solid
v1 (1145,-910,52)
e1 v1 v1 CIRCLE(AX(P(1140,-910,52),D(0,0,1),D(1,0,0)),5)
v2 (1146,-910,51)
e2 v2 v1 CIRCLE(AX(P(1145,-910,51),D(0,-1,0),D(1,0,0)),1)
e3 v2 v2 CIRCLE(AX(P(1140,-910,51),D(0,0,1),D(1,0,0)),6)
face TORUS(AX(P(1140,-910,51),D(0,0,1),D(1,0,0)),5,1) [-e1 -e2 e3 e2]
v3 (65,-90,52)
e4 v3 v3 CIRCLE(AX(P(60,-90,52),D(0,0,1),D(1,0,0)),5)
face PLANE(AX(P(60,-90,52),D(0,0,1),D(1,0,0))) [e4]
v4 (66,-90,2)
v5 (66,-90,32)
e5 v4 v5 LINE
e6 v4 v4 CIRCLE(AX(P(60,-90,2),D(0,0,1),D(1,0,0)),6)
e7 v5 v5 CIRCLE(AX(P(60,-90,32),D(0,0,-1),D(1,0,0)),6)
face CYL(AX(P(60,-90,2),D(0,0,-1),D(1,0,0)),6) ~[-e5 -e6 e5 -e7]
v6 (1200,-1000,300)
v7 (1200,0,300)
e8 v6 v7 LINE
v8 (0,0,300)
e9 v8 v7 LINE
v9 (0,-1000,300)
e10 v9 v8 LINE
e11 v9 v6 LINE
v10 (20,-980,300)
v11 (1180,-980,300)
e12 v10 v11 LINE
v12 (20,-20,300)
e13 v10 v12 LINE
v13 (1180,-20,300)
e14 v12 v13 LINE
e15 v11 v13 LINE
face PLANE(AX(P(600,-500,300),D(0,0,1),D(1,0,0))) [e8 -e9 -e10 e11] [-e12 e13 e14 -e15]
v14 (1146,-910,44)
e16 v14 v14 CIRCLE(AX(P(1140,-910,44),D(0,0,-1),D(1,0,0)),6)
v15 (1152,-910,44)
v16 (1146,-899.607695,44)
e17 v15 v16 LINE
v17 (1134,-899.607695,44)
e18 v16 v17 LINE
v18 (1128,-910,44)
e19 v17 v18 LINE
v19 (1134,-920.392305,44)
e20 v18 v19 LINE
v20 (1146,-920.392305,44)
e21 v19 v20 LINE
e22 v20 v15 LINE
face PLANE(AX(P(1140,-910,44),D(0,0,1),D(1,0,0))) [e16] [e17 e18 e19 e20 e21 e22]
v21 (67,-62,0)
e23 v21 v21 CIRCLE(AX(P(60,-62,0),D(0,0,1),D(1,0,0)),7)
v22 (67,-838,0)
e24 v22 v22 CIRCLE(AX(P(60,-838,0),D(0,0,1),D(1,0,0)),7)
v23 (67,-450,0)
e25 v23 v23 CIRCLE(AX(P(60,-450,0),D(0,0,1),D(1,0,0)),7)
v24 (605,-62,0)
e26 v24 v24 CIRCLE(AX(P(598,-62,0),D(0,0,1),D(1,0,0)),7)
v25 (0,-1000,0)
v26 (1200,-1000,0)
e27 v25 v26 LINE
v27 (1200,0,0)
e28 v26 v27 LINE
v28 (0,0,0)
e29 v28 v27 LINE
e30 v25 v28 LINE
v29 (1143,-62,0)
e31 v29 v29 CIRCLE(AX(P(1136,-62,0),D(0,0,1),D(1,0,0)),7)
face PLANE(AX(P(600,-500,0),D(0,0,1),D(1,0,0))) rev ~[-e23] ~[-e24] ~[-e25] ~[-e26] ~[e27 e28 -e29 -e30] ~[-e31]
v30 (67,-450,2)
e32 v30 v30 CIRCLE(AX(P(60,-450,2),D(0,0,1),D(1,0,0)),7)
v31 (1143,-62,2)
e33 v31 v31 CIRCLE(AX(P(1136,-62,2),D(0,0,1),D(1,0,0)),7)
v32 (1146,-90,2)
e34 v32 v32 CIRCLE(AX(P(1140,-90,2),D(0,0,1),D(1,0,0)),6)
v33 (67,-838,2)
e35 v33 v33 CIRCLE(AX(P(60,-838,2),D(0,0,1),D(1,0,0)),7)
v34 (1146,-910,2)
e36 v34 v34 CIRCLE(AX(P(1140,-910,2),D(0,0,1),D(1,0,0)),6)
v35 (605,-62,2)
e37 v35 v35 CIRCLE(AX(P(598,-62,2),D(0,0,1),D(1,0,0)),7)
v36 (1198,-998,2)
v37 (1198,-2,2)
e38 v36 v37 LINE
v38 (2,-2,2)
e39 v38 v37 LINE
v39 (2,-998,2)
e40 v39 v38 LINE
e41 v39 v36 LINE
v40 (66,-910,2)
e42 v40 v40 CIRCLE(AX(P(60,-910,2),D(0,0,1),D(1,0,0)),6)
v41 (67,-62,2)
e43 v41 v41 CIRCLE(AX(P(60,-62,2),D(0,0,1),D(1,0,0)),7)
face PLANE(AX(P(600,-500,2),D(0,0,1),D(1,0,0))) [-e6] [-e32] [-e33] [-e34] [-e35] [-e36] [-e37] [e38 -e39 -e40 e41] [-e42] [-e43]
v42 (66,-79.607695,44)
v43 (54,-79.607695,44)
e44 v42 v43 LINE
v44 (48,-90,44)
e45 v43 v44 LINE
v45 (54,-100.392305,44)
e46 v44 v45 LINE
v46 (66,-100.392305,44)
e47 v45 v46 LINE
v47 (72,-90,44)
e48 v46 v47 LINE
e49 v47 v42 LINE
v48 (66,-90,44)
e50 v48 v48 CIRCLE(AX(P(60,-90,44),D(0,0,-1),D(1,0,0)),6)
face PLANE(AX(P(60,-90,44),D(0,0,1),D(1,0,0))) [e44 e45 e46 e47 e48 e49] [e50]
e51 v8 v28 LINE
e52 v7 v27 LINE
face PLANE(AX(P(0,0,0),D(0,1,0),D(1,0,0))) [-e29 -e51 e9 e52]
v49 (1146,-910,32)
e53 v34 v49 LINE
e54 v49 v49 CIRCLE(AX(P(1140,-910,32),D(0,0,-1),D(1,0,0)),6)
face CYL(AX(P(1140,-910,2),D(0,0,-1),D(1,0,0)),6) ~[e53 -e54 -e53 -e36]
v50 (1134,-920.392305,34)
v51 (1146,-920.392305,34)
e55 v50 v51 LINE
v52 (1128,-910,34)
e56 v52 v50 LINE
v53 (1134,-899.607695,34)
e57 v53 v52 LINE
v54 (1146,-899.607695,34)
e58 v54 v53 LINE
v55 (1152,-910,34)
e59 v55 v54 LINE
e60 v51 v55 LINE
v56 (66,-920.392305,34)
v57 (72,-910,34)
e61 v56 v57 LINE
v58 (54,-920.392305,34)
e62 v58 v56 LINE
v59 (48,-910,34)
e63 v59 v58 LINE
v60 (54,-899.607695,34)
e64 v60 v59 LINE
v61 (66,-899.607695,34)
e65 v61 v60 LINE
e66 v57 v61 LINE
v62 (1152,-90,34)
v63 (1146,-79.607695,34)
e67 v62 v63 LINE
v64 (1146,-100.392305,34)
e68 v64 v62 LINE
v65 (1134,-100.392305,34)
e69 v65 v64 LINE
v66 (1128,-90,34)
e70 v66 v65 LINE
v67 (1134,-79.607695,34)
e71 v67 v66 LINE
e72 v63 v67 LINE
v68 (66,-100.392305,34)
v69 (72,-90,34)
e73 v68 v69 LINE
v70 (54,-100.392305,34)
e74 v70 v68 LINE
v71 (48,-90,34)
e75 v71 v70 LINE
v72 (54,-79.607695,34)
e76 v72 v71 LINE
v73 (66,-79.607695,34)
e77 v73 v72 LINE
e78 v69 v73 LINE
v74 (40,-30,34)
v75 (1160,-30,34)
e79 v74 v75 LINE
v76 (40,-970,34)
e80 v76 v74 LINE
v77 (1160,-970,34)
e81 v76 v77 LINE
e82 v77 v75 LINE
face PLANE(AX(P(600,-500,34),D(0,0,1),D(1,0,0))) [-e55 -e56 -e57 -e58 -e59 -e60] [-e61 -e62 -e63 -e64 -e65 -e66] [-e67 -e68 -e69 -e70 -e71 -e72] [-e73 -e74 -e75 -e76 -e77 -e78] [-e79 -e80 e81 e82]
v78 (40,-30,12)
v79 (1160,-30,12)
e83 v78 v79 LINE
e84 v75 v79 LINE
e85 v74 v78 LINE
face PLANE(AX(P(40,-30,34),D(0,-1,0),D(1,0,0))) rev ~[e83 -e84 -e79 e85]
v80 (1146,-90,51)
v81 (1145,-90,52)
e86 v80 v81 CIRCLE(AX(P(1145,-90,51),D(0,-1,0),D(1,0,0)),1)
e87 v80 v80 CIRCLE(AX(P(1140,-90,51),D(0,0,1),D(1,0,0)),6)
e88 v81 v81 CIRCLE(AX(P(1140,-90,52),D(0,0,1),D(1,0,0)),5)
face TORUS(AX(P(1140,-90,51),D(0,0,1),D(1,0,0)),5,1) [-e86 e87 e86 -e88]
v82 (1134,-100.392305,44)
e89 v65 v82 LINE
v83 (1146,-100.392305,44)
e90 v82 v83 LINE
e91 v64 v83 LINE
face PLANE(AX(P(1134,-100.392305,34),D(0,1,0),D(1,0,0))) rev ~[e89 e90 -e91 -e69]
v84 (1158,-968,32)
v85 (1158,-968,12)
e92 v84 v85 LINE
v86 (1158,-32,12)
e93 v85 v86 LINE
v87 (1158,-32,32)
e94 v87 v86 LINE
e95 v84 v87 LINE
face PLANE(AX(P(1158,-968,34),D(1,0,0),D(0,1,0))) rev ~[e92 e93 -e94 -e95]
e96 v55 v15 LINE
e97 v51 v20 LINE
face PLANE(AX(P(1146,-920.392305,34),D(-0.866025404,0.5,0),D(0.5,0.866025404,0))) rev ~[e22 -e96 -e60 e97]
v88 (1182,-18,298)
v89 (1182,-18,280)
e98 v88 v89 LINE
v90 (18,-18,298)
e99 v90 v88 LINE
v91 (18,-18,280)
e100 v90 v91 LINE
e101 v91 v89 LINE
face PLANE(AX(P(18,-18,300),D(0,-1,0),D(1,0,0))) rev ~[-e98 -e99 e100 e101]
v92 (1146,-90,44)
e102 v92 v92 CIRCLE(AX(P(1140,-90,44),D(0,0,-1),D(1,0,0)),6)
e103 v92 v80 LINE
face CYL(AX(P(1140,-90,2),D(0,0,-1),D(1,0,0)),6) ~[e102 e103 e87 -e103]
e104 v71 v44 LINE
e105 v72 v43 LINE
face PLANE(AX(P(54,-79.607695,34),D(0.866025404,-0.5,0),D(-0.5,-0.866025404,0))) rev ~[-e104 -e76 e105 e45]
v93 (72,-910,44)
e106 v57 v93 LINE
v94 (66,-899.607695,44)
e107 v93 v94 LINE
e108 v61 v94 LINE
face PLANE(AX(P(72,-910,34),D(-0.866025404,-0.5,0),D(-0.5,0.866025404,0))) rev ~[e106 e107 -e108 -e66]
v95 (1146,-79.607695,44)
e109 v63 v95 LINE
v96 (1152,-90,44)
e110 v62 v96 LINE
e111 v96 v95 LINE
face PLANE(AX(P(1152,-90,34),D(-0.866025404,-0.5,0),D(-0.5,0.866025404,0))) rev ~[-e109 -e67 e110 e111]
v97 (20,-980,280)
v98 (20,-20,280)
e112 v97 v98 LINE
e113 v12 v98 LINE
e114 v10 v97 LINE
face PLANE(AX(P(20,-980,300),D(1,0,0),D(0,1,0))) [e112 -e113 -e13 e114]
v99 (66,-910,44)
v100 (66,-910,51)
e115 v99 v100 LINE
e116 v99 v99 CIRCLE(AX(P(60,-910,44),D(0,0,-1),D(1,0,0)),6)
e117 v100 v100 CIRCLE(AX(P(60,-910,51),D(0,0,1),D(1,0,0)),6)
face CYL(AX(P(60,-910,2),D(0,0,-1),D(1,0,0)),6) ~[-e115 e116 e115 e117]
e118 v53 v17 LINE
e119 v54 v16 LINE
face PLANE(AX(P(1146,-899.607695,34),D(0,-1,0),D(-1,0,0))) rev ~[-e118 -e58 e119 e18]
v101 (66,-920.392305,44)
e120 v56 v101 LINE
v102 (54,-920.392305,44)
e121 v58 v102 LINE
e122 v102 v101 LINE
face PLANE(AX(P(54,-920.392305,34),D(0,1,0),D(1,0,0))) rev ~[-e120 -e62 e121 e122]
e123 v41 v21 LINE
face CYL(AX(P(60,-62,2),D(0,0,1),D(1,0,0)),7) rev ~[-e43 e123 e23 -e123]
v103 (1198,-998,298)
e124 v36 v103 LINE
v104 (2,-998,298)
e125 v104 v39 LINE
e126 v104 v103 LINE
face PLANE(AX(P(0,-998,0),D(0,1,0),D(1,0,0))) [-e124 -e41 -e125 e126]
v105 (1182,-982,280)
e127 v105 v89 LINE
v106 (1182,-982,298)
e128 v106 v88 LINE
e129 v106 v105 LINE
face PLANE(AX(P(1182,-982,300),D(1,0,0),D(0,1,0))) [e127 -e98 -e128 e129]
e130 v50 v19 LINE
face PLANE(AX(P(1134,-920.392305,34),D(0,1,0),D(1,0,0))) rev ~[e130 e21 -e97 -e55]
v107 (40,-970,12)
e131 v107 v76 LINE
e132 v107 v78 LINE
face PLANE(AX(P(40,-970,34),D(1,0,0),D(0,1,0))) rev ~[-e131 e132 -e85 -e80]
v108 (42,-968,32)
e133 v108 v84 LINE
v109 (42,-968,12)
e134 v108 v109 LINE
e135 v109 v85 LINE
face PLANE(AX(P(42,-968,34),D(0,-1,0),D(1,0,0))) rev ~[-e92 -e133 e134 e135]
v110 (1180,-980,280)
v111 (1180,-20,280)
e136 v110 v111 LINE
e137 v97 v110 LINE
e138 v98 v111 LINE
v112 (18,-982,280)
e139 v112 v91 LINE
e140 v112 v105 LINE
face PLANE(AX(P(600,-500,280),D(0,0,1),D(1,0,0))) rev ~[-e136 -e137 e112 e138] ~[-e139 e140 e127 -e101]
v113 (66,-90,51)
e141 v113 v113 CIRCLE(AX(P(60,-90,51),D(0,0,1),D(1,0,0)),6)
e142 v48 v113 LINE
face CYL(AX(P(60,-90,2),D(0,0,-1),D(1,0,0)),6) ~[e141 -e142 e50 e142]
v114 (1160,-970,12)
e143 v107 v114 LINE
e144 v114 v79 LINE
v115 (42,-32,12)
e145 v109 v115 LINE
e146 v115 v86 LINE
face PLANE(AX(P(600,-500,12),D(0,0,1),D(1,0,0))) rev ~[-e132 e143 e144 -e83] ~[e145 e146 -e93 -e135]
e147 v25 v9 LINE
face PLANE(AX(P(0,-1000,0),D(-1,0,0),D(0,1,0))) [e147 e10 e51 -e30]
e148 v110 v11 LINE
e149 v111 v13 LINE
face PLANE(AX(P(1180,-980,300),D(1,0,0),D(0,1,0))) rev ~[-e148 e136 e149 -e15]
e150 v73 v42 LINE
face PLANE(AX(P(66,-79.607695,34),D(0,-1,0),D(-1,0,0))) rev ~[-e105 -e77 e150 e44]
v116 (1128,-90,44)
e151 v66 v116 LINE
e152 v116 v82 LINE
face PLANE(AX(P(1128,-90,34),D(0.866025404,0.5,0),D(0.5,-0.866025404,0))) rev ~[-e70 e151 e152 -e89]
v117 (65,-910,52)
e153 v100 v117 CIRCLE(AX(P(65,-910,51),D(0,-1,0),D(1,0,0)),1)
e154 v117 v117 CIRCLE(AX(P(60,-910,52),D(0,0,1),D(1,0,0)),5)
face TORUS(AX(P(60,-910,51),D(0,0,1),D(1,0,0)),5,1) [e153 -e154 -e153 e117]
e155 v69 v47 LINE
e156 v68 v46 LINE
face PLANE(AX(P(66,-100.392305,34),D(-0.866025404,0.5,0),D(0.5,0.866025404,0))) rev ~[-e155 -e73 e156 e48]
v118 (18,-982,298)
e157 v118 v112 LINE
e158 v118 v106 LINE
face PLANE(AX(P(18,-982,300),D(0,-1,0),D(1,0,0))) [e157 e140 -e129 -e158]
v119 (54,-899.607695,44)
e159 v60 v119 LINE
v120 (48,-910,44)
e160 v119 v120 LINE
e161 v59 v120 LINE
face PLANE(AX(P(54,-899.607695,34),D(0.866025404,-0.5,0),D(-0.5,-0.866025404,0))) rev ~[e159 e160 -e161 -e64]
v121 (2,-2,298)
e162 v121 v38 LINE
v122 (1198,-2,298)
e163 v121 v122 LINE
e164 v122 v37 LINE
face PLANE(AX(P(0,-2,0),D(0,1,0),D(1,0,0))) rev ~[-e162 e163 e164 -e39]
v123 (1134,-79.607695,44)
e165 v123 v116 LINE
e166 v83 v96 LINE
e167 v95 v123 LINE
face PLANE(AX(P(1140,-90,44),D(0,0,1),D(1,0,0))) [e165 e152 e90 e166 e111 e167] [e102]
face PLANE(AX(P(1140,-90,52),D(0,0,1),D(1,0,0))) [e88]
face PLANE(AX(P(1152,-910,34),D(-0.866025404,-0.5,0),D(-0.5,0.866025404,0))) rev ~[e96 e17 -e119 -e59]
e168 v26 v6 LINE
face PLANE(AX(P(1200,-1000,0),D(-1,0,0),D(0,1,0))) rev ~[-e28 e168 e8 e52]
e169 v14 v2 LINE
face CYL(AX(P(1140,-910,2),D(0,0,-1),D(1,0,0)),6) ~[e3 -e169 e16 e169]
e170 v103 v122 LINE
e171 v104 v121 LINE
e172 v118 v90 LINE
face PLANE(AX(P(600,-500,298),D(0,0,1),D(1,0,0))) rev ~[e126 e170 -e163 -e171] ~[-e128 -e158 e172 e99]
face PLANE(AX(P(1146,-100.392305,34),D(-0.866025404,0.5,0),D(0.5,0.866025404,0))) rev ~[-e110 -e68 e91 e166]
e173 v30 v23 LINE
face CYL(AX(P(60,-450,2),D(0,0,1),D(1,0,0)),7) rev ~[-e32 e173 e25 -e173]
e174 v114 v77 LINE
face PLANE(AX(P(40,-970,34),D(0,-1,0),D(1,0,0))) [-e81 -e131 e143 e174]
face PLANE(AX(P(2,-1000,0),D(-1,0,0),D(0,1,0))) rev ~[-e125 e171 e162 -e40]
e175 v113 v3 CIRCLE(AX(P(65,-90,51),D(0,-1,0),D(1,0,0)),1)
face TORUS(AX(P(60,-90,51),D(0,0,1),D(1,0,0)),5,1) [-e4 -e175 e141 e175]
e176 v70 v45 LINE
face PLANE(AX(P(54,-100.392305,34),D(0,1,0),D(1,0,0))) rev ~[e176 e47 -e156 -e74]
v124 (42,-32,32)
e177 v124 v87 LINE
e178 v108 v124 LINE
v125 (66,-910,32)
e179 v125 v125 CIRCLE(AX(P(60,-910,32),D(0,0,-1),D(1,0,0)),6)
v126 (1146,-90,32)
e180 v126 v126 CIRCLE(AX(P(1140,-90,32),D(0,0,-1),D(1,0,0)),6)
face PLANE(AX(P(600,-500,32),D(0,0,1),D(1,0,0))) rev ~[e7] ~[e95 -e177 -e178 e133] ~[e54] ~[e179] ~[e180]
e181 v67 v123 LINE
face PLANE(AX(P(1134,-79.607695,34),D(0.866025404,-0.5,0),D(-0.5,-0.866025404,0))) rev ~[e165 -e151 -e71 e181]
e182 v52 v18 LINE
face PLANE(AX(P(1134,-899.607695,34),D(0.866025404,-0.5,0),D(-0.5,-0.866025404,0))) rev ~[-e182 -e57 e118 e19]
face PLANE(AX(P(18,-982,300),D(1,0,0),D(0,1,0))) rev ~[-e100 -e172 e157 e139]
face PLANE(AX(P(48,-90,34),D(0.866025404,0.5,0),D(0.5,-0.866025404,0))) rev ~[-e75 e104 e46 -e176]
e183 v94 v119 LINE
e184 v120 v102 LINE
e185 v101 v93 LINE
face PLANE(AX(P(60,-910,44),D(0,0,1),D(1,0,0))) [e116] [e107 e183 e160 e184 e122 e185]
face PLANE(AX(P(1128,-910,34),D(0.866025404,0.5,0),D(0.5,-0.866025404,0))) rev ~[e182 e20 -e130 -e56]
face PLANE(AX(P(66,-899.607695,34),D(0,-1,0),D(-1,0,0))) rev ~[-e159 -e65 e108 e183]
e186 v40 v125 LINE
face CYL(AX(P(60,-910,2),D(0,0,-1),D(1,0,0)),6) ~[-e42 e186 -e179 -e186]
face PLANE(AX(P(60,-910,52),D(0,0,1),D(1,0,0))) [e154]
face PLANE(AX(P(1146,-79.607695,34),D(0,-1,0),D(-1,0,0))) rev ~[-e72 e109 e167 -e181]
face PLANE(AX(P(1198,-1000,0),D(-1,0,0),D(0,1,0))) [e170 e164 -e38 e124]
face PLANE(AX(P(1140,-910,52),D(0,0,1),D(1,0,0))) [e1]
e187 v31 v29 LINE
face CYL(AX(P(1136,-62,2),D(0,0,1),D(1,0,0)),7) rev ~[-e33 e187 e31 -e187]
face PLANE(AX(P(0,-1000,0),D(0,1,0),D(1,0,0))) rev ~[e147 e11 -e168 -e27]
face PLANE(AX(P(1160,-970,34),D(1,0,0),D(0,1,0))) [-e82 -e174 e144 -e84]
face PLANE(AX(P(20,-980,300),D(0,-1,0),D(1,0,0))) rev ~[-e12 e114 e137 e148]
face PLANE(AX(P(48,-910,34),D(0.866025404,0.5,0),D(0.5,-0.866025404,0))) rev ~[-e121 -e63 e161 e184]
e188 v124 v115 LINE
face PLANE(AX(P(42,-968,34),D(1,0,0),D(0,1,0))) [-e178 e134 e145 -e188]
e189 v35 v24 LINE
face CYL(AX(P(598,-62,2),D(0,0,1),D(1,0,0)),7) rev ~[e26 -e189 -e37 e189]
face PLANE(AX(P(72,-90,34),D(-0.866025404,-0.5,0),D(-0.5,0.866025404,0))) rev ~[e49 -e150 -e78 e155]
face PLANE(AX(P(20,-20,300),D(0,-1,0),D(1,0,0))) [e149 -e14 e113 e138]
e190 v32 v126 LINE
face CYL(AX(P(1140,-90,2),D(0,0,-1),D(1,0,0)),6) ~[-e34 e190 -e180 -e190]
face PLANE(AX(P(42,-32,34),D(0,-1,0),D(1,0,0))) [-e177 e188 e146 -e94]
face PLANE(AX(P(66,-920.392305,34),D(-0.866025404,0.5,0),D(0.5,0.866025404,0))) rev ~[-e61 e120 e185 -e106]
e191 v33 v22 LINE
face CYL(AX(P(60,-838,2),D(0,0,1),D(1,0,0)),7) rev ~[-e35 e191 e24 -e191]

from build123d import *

# Parameters (mm, degrees)
SKETCH_1_W                     = 1200
SKETCH_1_H                     = 1000
EXTRUDE_1_DEPTH                = 300
SHELL_1_T                      = -2
SKETCH_2_R                     = 7
CUT_EXTRUDE_1_DEPTH            = 1591.221368238
PATTERN_LINEAR_1_COUNT         = 3
PATTERN_LINEAR_1_PITCH         = 388
PATTERN_LINEAR_2_COUNT         = 3
PATTERN_LINEAR_2_PITCH         = 538
SKETCH_3_W                     = 1200
SKETCH_3_H                     = 1000
SKETCH_3_W_2                   = 1160
SKETCH_3_H_2                   = 960
EXTRUDE_2_DEPTH                = 2
SKETCH_4_W                     = 1164
SKETCH_4_H                     = 964
SKETCH_4_W_2                   = 1160
SKETCH_4_H_2                   = 960
EXTRUDE_3_DEPTH                = 20
EXTRUDE_START                  = 30
SKETCH_5_W                     = 1120
SKETCH_5_H                     = 940
EXTRUDE_4_DEPTH                = 2
SKETCH_6_W                     = 1120
SKETCH_6_H                     = 940
SKETCH_6_W_2                   = 1116
SKETCH_6_H_2                   = 936
EXTRUDE_5_DEPTH                = 22
SKETCH_8_R                     = 6
EXTRUDE_6_DEPTH                = 50
FILLET_1_R                     = 1
EXTRUDE_7_DEPTH                = 10
PATTERN_LINEAR_4_COUNT         = 2
PATTERN_LINEAR_4_PITCH         = 1080
PATTERN_LINEAR_4_COUNT_DIR2    = 2
PATTERN_LINEAR_4_PITCH_DIR2    = 820
FILLET_1_OF_PATTERN_LINEAR_4_R = 1


with BuildPart() as part:
    # 草图1 → 凸台-拉伸1 (new body)
    with BuildSketch(Plane.XY):
        with Locations((600, -500)):
            Rectangle(SKETCH_1_W, SKETCH_1_H)
    extrude(amount=EXTRUDE_1_DEPTH)

    # 抽壳1
    shell_1_openings = [part.faces().sort_by_distance(p)[0] for p in [
        (600, -500, 300),
    ]]
    offset(amount=SHELL_1_T, openings=shell_1_openings, kind=Kind.INTERSECTION)

    # 草图2 → 切除-拉伸1 (cut, through all)
    with BuildSketch(Plane.XY.offset(2)):
        with Locations((60, -62)):
            Circle(SKETCH_2_R)
    cut_extrude_1 = extrude(amount=-CUT_EXTRUDE_1_DEPTH, mode=Mode.SUBTRACT)

    # 阵列(线性)1: 切除-拉伸1 ×3
    with Locations(*[(0, -i * PATTERN_LINEAR_1_PITCH, 0) for i in range(1, PATTERN_LINEAR_1_COUNT)]):
        add(cut_extrude_1, mode=Mode.SUBTRACT)

    # 阵列(线性)2: 切除-拉伸1 ×3
    with Locations(*[(i * PATTERN_LINEAR_2_PITCH, 0, 0) for i in range(1, PATTERN_LINEAR_2_COUNT)]):
        add(cut_extrude_1, mode=Mode.SUBTRACT)

    # 草图3 → 凸台-拉伸2 (add)
    with BuildSketch(Plane.XY.offset(300)):
        with Locations((600, -500)):
            Rectangle(SKETCH_3_W, SKETCH_3_H)
        with Locations((600, -500)):
            Rectangle(SKETCH_3_W_2, SKETCH_3_H_2, mode=Mode.SUBTRACT)
    extrude(amount=-EXTRUDE_2_DEPTH)

    # 草图4 → 凸台-拉伸3 (add)
    with BuildSketch(Plane.XY.offset(300)):
        with Locations((600, -500)):
            Rectangle(SKETCH_4_W, SKETCH_4_H)
        with Locations((600, -500)):
            Rectangle(SKETCH_4_W_2, SKETCH_4_H_2, mode=Mode.SUBTRACT)
    extrude(amount=-EXTRUDE_3_DEPTH)



with BuildPart() as body_2:
    # 草图5 → 凸台-拉伸4 (new body)
    with BuildSketch(Plane.XY.offset(2).offset(EXTRUDE_START)):
        with Locations((600, -500)):
            Rectangle(SKETCH_5_W, SKETCH_5_H)
    extrude(amount=EXTRUDE_4_DEPTH)

    # 草图6 → 凸台-拉伸5 (add)
    with BuildSketch(Plane.XY.offset(34)):
        with Locations((600, -500)):
            Rectangle(SKETCH_6_W, SKETCH_6_H)
        with Locations((600, -500)):
            Rectangle(SKETCH_6_W_2, SKETCH_6_H_2, mode=Mode.SUBTRACT)
    extrude(amount=-EXTRUDE_5_DEPTH)


with BuildPart() as part_1:
    add(part.part)

    add(body_2.part)  # 凸台-拉伸6 merges body 2
    # 草图8 → 凸台-拉伸6 (add)
    with BuildSketch(Plane.XY.offset(2)):
        with Locations((60, -90)):
            Circle(SKETCH_8_R)
    extrude_6 = extrude(amount=EXTRUDE_6_DEPTH)

    # 圆角1
    fillet_1_edges = [part_1.edges().sort_by_distance(p)[0] for p in [
        (54, -90, 52),
    ]]
    fillet(fillet_1_edges, radius=FILLET_1_R)

    # 草图9 → 凸台-拉伸7 (add)
    with BuildSketch(Plane.XY.offset(34)):
        Polygon((66, -79.607695155), (54, -79.607695155), (48, -90), (54, -100.392304845), (66, -100.392304845), (72, -90), align=None)
    extrude_7 = extrude(amount=EXTRUDE_7_DEPTH)

    # 阵列(线性)4: 凸台-拉伸6, Extrude 7 2 × 2
    with Locations(*[(i * PATTERN_LINEAR_4_PITCH, -j * PATTERN_LINEAR_4_PITCH_DIR2, 0) for i in range(PATTERN_LINEAR_4_COUNT) for j in range(PATTERN_LINEAR_4_COUNT_DIR2) if (i, j) != (0, 0)]):
        add(extrude_6)
        add(extrude_7)

    # 圆角1 of 阵列(线性)4
    fillet_1_of_pattern_linear_4_edges = [part_1.edges().sort_by_distance(p)[0] for p in [
        (54, -910, 52),
        (1134, -90, 52),
        (1134, -910, 52),
    ]]
    fillet(fillet_1_of_pattern_linear_4_edges, radius=FILLET_1_OF_PATTERN_LINEAR_4_R)


solid = part_1.part
